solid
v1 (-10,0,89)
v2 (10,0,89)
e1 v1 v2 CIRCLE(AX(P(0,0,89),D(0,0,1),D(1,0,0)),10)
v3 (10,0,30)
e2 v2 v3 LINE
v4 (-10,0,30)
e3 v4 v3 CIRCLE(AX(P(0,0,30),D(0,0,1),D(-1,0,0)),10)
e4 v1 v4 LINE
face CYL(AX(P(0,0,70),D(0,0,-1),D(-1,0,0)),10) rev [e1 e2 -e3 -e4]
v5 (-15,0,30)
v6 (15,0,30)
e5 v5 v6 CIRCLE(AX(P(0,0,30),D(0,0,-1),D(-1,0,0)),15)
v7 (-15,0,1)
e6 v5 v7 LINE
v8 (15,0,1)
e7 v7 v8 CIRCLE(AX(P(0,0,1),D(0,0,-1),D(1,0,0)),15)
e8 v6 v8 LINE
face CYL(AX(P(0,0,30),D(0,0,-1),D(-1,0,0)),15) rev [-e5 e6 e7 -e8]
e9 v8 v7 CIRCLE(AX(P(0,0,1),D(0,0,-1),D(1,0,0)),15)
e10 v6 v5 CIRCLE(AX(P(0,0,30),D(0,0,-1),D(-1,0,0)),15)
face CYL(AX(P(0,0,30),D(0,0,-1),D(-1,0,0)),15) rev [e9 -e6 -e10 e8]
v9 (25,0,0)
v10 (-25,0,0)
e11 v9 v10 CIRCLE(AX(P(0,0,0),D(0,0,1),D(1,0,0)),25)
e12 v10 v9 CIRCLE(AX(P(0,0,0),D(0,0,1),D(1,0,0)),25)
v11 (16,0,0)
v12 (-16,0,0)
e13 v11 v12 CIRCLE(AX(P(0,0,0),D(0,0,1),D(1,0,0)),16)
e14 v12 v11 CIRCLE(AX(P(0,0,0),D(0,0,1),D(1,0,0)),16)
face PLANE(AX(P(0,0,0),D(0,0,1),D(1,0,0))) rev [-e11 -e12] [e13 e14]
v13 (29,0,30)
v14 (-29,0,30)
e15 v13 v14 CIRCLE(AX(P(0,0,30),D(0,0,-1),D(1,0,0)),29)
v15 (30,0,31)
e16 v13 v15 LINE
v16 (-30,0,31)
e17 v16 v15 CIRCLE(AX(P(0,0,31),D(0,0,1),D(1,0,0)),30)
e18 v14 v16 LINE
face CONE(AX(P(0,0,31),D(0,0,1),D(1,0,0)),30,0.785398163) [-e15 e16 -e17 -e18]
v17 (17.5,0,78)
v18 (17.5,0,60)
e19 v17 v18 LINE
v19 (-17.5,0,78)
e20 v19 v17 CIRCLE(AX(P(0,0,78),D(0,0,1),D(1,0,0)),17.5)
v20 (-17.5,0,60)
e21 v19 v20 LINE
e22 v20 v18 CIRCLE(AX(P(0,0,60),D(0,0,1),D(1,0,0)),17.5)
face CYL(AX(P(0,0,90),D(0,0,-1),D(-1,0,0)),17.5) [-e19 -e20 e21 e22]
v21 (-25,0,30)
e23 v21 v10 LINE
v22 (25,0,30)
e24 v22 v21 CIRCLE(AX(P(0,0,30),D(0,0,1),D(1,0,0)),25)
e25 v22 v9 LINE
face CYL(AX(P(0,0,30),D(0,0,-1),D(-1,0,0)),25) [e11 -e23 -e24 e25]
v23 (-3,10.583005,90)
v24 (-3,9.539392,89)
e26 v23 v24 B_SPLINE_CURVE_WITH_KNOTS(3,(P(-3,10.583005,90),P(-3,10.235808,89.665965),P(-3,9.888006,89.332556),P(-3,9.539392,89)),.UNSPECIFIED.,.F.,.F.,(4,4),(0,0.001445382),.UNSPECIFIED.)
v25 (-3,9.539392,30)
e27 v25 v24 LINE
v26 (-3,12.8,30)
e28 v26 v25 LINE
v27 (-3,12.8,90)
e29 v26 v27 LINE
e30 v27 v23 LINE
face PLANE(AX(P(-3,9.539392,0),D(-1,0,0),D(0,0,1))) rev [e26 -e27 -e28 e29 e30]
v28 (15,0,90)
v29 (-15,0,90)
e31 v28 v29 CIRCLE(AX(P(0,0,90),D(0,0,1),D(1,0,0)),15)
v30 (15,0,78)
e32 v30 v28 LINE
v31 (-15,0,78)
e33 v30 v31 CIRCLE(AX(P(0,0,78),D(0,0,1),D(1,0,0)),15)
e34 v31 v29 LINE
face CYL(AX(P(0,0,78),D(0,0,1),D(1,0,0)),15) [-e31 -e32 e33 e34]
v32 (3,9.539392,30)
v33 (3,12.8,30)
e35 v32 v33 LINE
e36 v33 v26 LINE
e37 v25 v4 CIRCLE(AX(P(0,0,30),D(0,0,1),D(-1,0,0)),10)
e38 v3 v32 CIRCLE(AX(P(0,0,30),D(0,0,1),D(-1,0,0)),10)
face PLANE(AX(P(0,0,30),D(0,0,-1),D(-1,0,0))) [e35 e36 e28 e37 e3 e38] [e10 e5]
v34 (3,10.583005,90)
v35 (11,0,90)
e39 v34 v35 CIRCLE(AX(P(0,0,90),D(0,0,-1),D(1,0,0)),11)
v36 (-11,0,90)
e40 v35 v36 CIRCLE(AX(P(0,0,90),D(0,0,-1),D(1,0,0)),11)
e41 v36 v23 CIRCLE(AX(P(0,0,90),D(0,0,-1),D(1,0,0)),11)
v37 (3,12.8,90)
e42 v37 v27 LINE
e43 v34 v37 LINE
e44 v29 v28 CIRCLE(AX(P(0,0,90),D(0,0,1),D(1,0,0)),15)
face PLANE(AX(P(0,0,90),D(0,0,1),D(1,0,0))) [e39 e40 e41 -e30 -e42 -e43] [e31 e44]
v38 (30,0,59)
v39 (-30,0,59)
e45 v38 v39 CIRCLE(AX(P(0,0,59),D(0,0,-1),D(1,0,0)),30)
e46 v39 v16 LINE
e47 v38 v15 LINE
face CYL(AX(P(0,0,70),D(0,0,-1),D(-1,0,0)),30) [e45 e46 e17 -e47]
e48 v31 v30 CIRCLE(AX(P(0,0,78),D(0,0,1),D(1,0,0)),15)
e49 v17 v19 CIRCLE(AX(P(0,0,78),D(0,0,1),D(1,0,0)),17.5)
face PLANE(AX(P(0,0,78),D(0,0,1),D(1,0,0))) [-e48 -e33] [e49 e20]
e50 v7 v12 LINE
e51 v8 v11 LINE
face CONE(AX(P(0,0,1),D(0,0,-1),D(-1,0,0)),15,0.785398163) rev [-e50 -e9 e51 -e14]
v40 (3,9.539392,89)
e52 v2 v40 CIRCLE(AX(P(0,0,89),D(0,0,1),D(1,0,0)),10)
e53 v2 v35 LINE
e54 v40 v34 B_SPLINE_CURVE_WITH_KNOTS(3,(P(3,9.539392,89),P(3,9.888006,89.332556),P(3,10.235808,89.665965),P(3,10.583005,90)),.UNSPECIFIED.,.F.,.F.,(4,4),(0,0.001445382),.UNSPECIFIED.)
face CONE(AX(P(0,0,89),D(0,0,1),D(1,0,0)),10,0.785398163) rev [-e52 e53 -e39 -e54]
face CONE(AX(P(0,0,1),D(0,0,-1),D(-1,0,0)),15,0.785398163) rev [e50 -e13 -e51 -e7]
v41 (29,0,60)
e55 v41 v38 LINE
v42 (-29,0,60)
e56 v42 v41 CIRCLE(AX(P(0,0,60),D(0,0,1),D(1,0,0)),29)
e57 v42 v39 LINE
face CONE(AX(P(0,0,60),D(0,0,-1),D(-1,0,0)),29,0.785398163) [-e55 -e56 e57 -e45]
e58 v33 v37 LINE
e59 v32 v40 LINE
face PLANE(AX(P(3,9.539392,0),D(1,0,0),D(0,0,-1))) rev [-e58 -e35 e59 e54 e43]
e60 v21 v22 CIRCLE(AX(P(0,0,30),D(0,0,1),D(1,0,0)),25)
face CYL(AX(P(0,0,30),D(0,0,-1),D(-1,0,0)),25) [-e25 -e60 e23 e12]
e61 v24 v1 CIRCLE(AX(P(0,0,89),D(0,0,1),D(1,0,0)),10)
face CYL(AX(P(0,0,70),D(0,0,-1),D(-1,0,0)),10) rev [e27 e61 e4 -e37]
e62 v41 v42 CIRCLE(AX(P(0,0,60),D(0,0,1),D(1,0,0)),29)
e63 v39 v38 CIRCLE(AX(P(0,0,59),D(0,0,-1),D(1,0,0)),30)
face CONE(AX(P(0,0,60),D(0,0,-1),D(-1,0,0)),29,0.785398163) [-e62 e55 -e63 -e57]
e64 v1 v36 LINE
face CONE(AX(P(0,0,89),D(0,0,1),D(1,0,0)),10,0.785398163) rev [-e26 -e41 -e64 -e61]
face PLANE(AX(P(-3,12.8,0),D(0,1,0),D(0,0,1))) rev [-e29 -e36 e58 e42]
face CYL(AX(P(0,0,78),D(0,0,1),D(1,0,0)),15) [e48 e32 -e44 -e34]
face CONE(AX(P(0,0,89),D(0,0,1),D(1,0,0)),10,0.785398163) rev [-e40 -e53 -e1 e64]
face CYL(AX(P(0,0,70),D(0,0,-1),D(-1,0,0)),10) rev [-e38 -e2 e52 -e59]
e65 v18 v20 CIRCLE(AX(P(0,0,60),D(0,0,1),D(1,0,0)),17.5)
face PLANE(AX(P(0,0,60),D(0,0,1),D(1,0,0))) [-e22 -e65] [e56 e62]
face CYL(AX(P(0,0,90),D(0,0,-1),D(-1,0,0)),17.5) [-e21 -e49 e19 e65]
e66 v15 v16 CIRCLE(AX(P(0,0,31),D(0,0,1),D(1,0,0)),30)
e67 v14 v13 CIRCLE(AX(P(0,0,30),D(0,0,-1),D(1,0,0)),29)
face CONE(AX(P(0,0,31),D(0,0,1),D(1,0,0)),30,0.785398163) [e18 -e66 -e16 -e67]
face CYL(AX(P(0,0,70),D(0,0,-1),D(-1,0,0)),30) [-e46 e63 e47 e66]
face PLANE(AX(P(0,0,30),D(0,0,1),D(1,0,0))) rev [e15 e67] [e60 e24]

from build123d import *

# Parameters (mm, degrees)
SKETCH_1_R          = 25
EXTRUDE_1_DEPTH     = 30
SKETCH_2_R          = 30
EXTRUDE_2_DEPTH     = 40
SKETCH_4_R          = 10
CUT_EXTRUDE_1_DEPTH = 82.853527719
SKETCH_11_W         = 6
SKETCH_11_H         = 3.260607986
CUT_EXTRUDE_3_DEPTH = 82.853527719
SKETCH_12_R         = 15
CUT_EXTRUDE_4_DEPTH = 30
SKETCH_13_R         = 17.5
EXTRUDE_4_DEPTH     = 20
CUT_EXTRUDE_START   = -10
SKETCH_14_R         = 30
SKETCH_14_R_2       = 17.5
CUT_EXTRUDE_5_DEPTH = 10
CUT_EXTRUDE_START_2 = -12
SKETCH_15_R         = 17.5
SKETCH_15_R_2       = 15
CUT_EXTRUDE_6_DEPTH = 12
CHAMFER_2_SIZE      = 1


with BuildPart() as part:
    # 草图1 → 凸台-拉伸1 (new body)
    with BuildSketch(Plane.XY):
        Circle(SKETCH_1_R)
    extrude(amount=EXTRUDE_1_DEPTH)

    # 草图2 → 凸台-拉伸2 (add)
    with BuildSketch(Plane.XY.offset(30)):
        Circle(SKETCH_2_R)
    extrude(amount=EXTRUDE_2_DEPTH)

    # 草图4 → 切除-拉伸1 (cut, through all)
    with BuildSketch(Plane(origin=(0, 0, 0), x_dir=(-1, 0, 0), z_dir=(0, 0, -1))):
        Circle(SKETCH_4_R)
    extrude(amount=-CUT_EXTRUDE_1_DEPTH, mode=Mode.SUBTRACT)

    # 草图11 → 切除-拉伸3 (cut, through all)
    with BuildSketch(Plane.XY.offset(70)):
        with Locations((0, 11.169696007)):
            Rectangle(SKETCH_11_W, SKETCH_11_H)
    extrude(amount=-CUT_EXTRUDE_3_DEPTH, mode=Mode.SUBTRACT)

    # 草图12 → 切除-拉伸4 (cut)
    with BuildSketch(Plane(origin=(0, 0, 0), x_dir=(-1, 0, 0), z_dir=(0, 0, -1))):
        Circle(SKETCH_12_R)
    extrude(amount=-CUT_EXTRUDE_4_DEPTH, mode=Mode.SUBTRACT)

    # 草图13 → 凸台-拉伸4 (add)
    with BuildSketch(Plane.XY.offset(70)):
        Circle(SKETCH_13_R)
        with BuildLine():
            Line((3, 9.539392014), (3, 12.8))
            Line((3, 12.8), (-3, 12.8))
            Line((-3, 12.8), (-3, 9.539392014))
            ThreePointArc((-3, 9.539392014), (0, -10), (3, 9.539392014))
        make_face(mode=Mode.SUBTRACT)
    extrude(amount=EXTRUDE_4_DEPTH)

    # 草图14 → 切除-拉伸5 (cut)
    with BuildSketch(Plane.XY.offset(70).offset(CUT_EXTRUDE_START)):
        Circle(SKETCH_14_R)
        Circle(SKETCH_14_R_2, mode=Mode.SUBTRACT)
    extrude(amount=CUT_EXTRUDE_5_DEPTH, mode=Mode.SUBTRACT)

    # 草图15 → 切除-拉伸6 (cut)
    with BuildSketch(Plane.XY.offset(90).offset(CUT_EXTRUDE_START_2)):
        Circle(SKETCH_15_R)
        with Locations(Location((0, 0, 0), (0, 0, 180))):
            Circle(SKETCH_15_R_2, mode=Mode.SUBTRACT)
    extrude(amount=CUT_EXTRUDE_6_DEPTH, mode=Mode.SUBTRACT)

    # 倒角2
    chamfer_2_edges = [part.edges().sort_by_distance(p)[0] for p in [
        (15, 0, 0),
        (0, -10, 90),
        (-30, 0, 30),
        (-30, 0, 60),
    ]]
    chamfer(chamfer_2_edges, length=CHAMFER_2_SIZE)


solid = part.part
